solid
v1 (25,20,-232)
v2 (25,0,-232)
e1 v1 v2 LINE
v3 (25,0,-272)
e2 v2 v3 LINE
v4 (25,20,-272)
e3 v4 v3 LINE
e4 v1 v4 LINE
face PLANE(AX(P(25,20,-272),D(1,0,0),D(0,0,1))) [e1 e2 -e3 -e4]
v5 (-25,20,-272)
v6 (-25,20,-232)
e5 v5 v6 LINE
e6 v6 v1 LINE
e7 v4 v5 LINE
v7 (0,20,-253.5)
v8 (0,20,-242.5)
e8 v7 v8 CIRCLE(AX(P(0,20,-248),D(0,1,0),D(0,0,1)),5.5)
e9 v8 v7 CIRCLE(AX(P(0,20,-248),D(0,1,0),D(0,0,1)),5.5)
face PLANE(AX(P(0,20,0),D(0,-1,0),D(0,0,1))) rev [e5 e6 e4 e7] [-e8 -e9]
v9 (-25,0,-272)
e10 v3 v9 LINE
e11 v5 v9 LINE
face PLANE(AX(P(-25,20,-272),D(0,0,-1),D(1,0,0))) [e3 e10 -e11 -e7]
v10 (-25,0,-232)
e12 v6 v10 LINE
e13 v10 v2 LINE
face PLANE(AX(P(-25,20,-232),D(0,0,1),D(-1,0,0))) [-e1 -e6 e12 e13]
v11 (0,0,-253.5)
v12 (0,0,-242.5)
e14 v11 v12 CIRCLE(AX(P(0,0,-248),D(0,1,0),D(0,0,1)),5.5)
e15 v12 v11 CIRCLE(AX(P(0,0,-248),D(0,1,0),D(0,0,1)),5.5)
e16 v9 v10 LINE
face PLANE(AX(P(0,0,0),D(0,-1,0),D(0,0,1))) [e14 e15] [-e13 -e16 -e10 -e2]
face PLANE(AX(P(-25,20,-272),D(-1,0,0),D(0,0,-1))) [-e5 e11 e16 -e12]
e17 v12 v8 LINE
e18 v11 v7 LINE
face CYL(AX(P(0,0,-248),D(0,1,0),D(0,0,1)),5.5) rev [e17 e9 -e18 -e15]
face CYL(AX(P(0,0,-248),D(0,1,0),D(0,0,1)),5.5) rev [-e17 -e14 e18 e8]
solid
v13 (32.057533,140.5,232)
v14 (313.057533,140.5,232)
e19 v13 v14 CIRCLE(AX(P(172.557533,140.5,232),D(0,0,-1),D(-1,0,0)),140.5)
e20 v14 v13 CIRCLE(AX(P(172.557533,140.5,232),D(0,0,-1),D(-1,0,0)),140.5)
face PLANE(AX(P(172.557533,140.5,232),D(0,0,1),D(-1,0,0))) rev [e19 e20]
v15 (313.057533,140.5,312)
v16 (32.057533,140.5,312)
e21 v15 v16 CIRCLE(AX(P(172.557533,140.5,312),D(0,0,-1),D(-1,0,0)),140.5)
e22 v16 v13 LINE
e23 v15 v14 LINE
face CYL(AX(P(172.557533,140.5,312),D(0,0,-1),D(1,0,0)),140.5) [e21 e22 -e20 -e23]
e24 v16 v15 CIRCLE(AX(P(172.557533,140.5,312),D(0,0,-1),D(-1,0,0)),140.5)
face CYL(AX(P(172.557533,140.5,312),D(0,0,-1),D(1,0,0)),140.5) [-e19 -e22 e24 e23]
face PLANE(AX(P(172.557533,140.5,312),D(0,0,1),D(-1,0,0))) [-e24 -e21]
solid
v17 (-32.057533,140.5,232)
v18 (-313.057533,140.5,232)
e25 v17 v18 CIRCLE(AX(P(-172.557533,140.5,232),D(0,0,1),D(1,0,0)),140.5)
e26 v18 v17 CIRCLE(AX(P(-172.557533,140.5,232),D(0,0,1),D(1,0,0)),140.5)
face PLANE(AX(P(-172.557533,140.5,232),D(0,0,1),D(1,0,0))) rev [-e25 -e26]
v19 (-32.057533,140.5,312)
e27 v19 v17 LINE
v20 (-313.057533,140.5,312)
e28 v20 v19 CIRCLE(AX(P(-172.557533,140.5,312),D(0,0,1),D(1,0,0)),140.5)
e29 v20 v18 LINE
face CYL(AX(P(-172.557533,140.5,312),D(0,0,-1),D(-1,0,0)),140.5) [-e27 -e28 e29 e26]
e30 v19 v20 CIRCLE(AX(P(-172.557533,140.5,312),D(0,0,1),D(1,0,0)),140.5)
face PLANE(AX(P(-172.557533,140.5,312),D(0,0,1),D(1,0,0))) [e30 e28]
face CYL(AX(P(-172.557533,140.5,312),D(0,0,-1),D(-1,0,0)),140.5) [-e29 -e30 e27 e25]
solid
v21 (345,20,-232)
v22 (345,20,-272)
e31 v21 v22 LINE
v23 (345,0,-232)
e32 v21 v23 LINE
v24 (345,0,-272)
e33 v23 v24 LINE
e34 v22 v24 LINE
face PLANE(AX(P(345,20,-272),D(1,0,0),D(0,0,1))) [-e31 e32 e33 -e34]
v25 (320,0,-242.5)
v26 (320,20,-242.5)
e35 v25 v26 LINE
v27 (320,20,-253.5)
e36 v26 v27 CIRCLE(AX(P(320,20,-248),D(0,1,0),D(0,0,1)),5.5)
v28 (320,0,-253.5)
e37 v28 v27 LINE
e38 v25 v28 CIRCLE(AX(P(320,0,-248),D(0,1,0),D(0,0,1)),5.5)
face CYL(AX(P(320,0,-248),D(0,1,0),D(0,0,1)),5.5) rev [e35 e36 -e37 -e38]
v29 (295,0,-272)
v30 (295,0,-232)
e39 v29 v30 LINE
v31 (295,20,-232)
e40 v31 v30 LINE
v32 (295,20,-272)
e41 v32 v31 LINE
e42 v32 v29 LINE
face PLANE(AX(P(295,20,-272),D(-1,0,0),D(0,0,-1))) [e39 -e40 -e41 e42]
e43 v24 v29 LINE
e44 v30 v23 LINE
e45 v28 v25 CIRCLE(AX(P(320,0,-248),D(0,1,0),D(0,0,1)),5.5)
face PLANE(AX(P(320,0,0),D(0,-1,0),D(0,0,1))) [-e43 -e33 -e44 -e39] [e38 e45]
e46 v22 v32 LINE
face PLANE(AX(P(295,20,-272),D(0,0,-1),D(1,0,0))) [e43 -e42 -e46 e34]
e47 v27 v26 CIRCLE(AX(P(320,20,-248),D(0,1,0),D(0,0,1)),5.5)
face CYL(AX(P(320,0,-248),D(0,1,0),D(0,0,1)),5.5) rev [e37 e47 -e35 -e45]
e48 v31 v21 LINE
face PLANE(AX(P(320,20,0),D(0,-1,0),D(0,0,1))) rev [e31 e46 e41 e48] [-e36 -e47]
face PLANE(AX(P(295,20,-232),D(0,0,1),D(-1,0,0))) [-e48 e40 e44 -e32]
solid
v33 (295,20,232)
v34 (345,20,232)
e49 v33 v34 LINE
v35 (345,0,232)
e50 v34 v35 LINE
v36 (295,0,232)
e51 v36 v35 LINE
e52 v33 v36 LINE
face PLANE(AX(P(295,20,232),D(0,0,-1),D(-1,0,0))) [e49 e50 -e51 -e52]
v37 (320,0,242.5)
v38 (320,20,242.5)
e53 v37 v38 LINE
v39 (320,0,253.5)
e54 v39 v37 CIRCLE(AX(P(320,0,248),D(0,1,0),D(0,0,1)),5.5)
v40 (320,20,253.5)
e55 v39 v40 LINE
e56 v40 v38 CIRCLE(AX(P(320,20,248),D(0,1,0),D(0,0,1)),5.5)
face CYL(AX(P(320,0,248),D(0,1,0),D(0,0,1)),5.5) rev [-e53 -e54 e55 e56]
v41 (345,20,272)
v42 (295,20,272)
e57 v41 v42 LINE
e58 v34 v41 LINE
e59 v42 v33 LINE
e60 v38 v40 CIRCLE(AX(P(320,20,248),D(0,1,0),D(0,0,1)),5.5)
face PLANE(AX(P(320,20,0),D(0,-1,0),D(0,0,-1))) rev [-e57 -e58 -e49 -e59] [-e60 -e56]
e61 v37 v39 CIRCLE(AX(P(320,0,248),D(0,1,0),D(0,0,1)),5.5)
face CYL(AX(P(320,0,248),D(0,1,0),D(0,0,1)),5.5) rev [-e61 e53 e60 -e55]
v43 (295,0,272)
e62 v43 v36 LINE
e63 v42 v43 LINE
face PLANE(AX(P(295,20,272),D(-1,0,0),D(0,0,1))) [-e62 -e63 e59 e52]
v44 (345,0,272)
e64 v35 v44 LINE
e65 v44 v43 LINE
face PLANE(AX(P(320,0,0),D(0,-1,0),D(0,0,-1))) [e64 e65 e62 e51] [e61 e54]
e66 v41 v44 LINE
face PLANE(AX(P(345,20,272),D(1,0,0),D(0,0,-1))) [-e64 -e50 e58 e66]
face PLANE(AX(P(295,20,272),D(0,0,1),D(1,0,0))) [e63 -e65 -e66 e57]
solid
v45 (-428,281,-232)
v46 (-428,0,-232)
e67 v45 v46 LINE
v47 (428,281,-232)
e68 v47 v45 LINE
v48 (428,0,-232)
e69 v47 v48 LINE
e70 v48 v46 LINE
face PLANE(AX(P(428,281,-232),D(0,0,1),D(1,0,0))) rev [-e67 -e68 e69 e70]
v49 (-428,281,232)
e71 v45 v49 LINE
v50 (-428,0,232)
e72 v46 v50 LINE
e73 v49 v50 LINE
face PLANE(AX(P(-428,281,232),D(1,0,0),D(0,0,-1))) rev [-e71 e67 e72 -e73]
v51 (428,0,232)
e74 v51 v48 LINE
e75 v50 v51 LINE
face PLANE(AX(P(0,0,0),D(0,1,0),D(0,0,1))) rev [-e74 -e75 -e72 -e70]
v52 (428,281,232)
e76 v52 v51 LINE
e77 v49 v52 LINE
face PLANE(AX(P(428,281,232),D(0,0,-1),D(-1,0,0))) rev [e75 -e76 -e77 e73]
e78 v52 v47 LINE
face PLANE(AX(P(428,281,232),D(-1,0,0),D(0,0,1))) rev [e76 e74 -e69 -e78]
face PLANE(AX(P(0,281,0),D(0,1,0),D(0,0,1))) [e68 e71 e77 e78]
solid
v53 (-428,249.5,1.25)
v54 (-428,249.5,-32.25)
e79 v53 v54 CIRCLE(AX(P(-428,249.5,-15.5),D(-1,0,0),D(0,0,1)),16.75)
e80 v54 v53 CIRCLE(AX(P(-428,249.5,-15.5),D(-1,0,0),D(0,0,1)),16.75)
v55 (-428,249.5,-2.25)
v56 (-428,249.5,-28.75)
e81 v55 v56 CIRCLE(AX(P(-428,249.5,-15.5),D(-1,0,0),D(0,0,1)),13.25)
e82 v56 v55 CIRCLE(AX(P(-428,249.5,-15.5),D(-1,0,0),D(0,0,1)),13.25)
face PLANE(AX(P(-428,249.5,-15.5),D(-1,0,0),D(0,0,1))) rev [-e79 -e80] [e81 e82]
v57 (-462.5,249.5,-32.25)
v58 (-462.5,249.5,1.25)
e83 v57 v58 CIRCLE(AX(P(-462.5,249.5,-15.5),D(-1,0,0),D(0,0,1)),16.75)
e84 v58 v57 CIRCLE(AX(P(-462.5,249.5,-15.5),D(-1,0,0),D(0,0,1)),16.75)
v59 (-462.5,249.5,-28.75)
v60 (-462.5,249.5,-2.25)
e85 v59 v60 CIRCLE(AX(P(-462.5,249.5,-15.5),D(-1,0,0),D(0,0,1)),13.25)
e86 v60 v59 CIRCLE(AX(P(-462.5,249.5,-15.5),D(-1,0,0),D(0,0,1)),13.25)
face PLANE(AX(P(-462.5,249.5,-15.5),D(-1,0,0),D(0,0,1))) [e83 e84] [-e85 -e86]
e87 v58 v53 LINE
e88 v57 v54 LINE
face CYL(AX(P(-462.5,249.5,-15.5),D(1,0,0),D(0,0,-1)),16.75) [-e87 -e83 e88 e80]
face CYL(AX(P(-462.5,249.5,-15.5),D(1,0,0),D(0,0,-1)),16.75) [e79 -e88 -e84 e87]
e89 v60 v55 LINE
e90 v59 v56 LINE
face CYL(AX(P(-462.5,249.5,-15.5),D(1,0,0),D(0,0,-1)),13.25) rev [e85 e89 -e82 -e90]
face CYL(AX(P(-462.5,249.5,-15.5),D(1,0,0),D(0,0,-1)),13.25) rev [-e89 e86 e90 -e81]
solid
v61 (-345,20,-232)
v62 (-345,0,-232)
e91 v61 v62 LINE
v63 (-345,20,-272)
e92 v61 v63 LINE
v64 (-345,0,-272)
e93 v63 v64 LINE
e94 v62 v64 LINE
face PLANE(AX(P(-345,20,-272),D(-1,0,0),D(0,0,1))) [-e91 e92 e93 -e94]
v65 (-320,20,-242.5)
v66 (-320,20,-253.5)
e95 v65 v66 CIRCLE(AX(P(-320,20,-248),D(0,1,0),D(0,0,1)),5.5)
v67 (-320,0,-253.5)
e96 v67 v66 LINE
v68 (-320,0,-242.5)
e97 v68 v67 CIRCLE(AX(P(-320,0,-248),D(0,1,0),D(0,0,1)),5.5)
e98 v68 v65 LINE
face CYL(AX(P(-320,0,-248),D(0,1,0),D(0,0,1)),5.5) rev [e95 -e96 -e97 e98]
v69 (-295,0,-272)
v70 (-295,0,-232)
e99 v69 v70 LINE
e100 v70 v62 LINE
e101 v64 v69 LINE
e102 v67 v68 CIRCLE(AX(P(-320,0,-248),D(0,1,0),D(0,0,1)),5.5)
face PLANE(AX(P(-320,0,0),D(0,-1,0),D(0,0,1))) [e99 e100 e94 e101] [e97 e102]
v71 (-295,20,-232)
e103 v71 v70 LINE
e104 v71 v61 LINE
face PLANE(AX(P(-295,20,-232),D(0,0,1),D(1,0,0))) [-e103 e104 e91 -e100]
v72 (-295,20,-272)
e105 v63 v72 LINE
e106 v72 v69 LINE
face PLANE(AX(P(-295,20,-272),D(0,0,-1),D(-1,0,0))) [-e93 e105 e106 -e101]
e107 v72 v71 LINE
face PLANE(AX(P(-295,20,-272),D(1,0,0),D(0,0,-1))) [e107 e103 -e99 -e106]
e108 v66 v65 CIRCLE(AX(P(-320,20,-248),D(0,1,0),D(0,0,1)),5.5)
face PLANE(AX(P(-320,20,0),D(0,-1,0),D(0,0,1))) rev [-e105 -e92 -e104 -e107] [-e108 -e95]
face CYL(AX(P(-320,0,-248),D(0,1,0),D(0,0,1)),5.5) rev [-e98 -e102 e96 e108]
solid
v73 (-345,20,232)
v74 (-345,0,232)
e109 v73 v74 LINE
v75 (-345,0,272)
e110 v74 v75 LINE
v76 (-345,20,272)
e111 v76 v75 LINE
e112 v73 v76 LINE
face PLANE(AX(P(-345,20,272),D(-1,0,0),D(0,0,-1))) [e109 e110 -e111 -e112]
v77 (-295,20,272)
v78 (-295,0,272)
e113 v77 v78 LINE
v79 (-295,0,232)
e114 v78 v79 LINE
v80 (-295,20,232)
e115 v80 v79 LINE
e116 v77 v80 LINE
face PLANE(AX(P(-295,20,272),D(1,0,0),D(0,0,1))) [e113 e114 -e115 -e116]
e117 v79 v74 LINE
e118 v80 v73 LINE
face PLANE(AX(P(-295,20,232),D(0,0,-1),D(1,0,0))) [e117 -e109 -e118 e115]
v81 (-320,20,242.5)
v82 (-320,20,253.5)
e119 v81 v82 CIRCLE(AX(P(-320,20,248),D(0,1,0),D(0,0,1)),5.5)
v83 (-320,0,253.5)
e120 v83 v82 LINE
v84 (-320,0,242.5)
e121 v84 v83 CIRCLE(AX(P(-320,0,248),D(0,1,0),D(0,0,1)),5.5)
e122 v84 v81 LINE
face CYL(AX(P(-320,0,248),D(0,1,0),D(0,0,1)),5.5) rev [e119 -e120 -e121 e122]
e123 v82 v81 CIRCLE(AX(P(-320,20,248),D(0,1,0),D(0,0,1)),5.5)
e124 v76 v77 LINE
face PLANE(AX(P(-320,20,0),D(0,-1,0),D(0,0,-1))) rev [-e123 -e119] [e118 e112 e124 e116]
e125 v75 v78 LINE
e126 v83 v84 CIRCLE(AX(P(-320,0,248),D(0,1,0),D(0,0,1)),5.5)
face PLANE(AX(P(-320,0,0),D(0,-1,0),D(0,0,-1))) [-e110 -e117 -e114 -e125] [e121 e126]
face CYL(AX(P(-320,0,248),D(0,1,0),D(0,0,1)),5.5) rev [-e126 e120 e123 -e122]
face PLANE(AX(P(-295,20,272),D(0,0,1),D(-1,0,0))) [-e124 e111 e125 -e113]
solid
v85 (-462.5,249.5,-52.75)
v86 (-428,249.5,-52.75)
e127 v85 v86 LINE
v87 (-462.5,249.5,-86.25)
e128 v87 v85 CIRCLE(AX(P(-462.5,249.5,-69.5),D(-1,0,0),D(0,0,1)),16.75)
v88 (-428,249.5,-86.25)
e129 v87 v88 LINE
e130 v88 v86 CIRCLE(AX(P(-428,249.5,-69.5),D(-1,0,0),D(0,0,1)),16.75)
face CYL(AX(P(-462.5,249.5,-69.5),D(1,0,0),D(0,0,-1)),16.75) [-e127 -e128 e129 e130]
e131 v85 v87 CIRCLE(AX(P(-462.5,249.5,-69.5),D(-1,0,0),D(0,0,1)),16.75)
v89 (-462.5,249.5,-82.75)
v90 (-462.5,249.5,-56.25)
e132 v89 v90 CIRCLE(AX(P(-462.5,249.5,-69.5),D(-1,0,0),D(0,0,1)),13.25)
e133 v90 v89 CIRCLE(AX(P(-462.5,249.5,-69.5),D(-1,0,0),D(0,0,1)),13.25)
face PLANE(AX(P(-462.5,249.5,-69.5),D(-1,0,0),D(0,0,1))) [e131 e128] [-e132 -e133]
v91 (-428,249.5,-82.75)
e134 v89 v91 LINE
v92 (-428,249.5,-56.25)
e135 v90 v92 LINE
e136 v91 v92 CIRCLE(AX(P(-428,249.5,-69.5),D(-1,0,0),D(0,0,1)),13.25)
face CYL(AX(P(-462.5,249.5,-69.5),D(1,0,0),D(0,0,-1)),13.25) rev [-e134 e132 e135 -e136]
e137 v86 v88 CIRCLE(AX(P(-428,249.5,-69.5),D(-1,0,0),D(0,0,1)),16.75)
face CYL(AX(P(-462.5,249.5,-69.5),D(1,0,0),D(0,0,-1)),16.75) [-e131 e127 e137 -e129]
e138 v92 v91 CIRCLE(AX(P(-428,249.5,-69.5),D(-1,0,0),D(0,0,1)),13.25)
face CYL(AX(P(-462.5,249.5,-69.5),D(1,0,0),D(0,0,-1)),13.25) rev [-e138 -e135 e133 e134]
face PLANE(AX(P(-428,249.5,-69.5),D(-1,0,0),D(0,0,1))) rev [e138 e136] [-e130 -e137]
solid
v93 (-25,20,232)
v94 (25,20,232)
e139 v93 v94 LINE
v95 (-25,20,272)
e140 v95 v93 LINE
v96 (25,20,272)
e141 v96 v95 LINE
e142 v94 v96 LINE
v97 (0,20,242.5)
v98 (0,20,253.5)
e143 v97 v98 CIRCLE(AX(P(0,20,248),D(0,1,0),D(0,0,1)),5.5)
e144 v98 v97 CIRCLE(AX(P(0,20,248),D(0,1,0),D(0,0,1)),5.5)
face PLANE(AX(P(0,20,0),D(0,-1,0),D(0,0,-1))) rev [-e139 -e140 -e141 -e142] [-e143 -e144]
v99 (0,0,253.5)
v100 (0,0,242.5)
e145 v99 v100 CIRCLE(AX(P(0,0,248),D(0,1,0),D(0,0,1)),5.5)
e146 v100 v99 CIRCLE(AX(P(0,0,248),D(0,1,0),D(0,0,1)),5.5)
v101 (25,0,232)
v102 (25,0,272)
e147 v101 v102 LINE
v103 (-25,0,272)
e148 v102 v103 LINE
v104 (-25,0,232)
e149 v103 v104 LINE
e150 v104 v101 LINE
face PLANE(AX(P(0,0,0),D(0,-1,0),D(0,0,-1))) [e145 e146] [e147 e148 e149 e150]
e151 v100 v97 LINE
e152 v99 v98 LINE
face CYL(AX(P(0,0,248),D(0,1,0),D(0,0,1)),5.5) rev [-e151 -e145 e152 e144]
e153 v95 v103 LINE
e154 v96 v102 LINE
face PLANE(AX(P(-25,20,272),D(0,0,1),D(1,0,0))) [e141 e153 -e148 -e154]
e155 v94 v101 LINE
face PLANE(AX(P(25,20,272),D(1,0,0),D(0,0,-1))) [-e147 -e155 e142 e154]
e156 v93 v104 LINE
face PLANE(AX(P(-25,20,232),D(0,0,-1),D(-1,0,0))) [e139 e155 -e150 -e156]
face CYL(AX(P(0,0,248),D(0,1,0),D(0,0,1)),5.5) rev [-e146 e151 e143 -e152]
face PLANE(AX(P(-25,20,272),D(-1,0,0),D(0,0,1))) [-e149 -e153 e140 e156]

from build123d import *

# Parameters (mm, degrees)
SKETCH_1_W             = 856
SKETCH_1_H             = 464
EXTRUDE_1_DEPTH        = 281
SKETCH_3_W             = 50
SKETCH_3_H             = 40
EXTRUDE_2_DEPTH        = 20
PATTERN_LINEAR_2_COUNT = 2
PATTERN_LINEAR_2_PITCH = 320
SKETCH_4_R             = 5.5
CUT_EXTRUDE_1_DEPTH    = 571.341125994
SKETCH_5_R             = 140.5
EXTRUDE_3_DEPTH        = 80
SKETCH_6_R             = 16.75
SKETCH_6_R_2           = 13.25
EXTRUDE_4_DEPTH        = 34.5
PATTERN_LINEAR_3_COUNT = 2
PATTERN_LINEAR_3_PITCH = 54


with BuildPart() as part:
    # 草图1 → 凸台-拉伸1 (new body)
    with BuildSketch(Plane(origin=(0, 0, 0), x_dir=(1, 0, 0), z_dir=(0, 1, 0))):
        Rectangle(SKETCH_1_W, SKETCH_1_H)
    extrude(amount=EXTRUDE_1_DEPTH)


with BuildPart() as body_2:
    # 草图3 → 凸台-拉伸2 (new body)
    with BuildSketch(Plane.XZ):
        with Locations((0, 252)):
            Rectangle(SKETCH_3_W, SKETCH_3_H)
    extrude(amount=-EXTRUDE_2_DEPTH)


with BuildPart() as body_3:
    # 镜向1: mirrored copy
    add(body_2.part.mirror(Plane.XY))


with BuildPart() as pattern_linear_2_1:
    # 阵列(线性)2: pattern copy
    add(body_2.part.moved(Location(Vector(1, 0, 0) * (1 * PATTERN_LINEAR_2_PITCH))))


with BuildPart() as pattern_linear_2_2:
    # 阵列(线性)2: pattern copy
    add(body_3.part.moved(Location(Vector(1, 0, 0) * (1 * PATTERN_LINEAR_2_PITCH))))


with BuildPart() as body_6:
    # 镜向2: mirrored copy
    add(pattern_linear_2_1.part.mirror(Plane(origin=(0, 0, 0), x_dir=(0, 0, 1), z_dir=(1, 0, 0))))


with BuildPart() as body_7:
    # Mirror 2 2: mirrored copy
    add(pattern_linear_2_2.part.mirror(Plane(origin=(0, 0, 0), x_dir=(0, 0, 1), z_dir=(1, 0, 0))))


with BuildPart() as cut_extrude_1_tool:
    # 草图4 → 切除-拉伸1 (new, through all)
    with BuildSketch(Plane(origin=(0, 20, 0), x_dir=(1, 0, 0), z_dir=(0, 1, 0))):
        with Locations(Location((-320, 248, 0), (0, 0, 270))):
            Circle(SKETCH_4_R)
        with Locations(Location((0, 248, 0), (0, 0, 270))):
            Circle(SKETCH_4_R)
        with Locations(Location((320, 248, 0), (0, 0, 270))):
            Circle(SKETCH_4_R)
        with Locations(Location((0, -248, 0), (0, 0, 270))):
            Circle(SKETCH_4_R)
        with Locations(Location((320, -248, 0), (0, 0, 270))):
            Circle(SKETCH_4_R)
        with Locations(Location((-320, -248, 0), (0, 0, 270))):
            Circle(SKETCH_4_R)
    extrude(amount=-CUT_EXTRUDE_1_DEPTH)


with BuildPart() as body_2_1:
    add(body_2.part)

    # 切除-拉伸1: cut by cut_extrude_1_tool
    add(cut_extrude_1_tool.part, mode=Mode.SUBTRACT)


with BuildPart() as body_3_1:
    add(body_3.part)

    # 切除-拉伸1: cut by cut_extrude_1_tool
    add(cut_extrude_1_tool.part, mode=Mode.SUBTRACT)


with BuildPart() as pattern_linear_2_1_1:
    add(pattern_linear_2_1.part)

    # 切除-拉伸1: cut by cut_extrude_1_tool
    add(cut_extrude_1_tool.part, mode=Mode.SUBTRACT)


with BuildPart() as pattern_linear_2_2_1:
    add(pattern_linear_2_2.part)

    # 切除-拉伸1: cut by cut_extrude_1_tool
    add(cut_extrude_1_tool.part, mode=Mode.SUBTRACT)


with BuildPart() as body_6_1:
    add(body_6.part)

    # 切除-拉伸1: cut by cut_extrude_1_tool
    add(cut_extrude_1_tool.part, mode=Mode.SUBTRACT)


with BuildPart() as body_7_1:
    add(body_7.part)

    # 切除-拉伸1: cut by cut_extrude_1_tool
    add(cut_extrude_1_tool.part, mode=Mode.SUBTRACT)


with BuildPart() as body_8:
    # 草图5 → 凸台-拉伸3 (new body)
    with BuildSketch(Plane.XY.offset(232)):
        with Locations((-172.55753304, 140.5)):
            Circle(SKETCH_5_R)
    extrude(amount=EXTRUDE_3_DEPTH)


with BuildPart() as body_9:
    # 镜向3: mirrored copy
    add(body_8.part.mirror(Plane(origin=(0, 0, 0), x_dir=(0, 0, 1), z_dir=(1, 0, 0))))


with BuildPart() as body_10:
    # 草图6 → 凸台-拉伸4 (new body)
    with BuildSketch(Plane.ZY.offset(428)):
        with Locations((-69.5, 249.5)):
            Circle(SKETCH_6_R)
        with Locations((-69.5, 249.5)):
            Circle(SKETCH_6_R_2, mode=Mode.SUBTRACT)
    extrude(amount=EXTRUDE_4_DEPTH)


with BuildPart() as pattern_linear_3_1:
    # 阵列(线性)3: pattern copy
    add(body_10.part.moved(Location(Vector(0, 0, 1) * (1 * PATTERN_LINEAR_3_PITCH))))


solid = Compound([part.part, body_2_1.part, body_3_1.part, pattern_linear_2_1_1.part, pattern_linear_2_2_1.part, body_6_1.part, body_7_1.part, body_8.part, body_9.part, body_10.part, pattern_linear_3_1.part])
